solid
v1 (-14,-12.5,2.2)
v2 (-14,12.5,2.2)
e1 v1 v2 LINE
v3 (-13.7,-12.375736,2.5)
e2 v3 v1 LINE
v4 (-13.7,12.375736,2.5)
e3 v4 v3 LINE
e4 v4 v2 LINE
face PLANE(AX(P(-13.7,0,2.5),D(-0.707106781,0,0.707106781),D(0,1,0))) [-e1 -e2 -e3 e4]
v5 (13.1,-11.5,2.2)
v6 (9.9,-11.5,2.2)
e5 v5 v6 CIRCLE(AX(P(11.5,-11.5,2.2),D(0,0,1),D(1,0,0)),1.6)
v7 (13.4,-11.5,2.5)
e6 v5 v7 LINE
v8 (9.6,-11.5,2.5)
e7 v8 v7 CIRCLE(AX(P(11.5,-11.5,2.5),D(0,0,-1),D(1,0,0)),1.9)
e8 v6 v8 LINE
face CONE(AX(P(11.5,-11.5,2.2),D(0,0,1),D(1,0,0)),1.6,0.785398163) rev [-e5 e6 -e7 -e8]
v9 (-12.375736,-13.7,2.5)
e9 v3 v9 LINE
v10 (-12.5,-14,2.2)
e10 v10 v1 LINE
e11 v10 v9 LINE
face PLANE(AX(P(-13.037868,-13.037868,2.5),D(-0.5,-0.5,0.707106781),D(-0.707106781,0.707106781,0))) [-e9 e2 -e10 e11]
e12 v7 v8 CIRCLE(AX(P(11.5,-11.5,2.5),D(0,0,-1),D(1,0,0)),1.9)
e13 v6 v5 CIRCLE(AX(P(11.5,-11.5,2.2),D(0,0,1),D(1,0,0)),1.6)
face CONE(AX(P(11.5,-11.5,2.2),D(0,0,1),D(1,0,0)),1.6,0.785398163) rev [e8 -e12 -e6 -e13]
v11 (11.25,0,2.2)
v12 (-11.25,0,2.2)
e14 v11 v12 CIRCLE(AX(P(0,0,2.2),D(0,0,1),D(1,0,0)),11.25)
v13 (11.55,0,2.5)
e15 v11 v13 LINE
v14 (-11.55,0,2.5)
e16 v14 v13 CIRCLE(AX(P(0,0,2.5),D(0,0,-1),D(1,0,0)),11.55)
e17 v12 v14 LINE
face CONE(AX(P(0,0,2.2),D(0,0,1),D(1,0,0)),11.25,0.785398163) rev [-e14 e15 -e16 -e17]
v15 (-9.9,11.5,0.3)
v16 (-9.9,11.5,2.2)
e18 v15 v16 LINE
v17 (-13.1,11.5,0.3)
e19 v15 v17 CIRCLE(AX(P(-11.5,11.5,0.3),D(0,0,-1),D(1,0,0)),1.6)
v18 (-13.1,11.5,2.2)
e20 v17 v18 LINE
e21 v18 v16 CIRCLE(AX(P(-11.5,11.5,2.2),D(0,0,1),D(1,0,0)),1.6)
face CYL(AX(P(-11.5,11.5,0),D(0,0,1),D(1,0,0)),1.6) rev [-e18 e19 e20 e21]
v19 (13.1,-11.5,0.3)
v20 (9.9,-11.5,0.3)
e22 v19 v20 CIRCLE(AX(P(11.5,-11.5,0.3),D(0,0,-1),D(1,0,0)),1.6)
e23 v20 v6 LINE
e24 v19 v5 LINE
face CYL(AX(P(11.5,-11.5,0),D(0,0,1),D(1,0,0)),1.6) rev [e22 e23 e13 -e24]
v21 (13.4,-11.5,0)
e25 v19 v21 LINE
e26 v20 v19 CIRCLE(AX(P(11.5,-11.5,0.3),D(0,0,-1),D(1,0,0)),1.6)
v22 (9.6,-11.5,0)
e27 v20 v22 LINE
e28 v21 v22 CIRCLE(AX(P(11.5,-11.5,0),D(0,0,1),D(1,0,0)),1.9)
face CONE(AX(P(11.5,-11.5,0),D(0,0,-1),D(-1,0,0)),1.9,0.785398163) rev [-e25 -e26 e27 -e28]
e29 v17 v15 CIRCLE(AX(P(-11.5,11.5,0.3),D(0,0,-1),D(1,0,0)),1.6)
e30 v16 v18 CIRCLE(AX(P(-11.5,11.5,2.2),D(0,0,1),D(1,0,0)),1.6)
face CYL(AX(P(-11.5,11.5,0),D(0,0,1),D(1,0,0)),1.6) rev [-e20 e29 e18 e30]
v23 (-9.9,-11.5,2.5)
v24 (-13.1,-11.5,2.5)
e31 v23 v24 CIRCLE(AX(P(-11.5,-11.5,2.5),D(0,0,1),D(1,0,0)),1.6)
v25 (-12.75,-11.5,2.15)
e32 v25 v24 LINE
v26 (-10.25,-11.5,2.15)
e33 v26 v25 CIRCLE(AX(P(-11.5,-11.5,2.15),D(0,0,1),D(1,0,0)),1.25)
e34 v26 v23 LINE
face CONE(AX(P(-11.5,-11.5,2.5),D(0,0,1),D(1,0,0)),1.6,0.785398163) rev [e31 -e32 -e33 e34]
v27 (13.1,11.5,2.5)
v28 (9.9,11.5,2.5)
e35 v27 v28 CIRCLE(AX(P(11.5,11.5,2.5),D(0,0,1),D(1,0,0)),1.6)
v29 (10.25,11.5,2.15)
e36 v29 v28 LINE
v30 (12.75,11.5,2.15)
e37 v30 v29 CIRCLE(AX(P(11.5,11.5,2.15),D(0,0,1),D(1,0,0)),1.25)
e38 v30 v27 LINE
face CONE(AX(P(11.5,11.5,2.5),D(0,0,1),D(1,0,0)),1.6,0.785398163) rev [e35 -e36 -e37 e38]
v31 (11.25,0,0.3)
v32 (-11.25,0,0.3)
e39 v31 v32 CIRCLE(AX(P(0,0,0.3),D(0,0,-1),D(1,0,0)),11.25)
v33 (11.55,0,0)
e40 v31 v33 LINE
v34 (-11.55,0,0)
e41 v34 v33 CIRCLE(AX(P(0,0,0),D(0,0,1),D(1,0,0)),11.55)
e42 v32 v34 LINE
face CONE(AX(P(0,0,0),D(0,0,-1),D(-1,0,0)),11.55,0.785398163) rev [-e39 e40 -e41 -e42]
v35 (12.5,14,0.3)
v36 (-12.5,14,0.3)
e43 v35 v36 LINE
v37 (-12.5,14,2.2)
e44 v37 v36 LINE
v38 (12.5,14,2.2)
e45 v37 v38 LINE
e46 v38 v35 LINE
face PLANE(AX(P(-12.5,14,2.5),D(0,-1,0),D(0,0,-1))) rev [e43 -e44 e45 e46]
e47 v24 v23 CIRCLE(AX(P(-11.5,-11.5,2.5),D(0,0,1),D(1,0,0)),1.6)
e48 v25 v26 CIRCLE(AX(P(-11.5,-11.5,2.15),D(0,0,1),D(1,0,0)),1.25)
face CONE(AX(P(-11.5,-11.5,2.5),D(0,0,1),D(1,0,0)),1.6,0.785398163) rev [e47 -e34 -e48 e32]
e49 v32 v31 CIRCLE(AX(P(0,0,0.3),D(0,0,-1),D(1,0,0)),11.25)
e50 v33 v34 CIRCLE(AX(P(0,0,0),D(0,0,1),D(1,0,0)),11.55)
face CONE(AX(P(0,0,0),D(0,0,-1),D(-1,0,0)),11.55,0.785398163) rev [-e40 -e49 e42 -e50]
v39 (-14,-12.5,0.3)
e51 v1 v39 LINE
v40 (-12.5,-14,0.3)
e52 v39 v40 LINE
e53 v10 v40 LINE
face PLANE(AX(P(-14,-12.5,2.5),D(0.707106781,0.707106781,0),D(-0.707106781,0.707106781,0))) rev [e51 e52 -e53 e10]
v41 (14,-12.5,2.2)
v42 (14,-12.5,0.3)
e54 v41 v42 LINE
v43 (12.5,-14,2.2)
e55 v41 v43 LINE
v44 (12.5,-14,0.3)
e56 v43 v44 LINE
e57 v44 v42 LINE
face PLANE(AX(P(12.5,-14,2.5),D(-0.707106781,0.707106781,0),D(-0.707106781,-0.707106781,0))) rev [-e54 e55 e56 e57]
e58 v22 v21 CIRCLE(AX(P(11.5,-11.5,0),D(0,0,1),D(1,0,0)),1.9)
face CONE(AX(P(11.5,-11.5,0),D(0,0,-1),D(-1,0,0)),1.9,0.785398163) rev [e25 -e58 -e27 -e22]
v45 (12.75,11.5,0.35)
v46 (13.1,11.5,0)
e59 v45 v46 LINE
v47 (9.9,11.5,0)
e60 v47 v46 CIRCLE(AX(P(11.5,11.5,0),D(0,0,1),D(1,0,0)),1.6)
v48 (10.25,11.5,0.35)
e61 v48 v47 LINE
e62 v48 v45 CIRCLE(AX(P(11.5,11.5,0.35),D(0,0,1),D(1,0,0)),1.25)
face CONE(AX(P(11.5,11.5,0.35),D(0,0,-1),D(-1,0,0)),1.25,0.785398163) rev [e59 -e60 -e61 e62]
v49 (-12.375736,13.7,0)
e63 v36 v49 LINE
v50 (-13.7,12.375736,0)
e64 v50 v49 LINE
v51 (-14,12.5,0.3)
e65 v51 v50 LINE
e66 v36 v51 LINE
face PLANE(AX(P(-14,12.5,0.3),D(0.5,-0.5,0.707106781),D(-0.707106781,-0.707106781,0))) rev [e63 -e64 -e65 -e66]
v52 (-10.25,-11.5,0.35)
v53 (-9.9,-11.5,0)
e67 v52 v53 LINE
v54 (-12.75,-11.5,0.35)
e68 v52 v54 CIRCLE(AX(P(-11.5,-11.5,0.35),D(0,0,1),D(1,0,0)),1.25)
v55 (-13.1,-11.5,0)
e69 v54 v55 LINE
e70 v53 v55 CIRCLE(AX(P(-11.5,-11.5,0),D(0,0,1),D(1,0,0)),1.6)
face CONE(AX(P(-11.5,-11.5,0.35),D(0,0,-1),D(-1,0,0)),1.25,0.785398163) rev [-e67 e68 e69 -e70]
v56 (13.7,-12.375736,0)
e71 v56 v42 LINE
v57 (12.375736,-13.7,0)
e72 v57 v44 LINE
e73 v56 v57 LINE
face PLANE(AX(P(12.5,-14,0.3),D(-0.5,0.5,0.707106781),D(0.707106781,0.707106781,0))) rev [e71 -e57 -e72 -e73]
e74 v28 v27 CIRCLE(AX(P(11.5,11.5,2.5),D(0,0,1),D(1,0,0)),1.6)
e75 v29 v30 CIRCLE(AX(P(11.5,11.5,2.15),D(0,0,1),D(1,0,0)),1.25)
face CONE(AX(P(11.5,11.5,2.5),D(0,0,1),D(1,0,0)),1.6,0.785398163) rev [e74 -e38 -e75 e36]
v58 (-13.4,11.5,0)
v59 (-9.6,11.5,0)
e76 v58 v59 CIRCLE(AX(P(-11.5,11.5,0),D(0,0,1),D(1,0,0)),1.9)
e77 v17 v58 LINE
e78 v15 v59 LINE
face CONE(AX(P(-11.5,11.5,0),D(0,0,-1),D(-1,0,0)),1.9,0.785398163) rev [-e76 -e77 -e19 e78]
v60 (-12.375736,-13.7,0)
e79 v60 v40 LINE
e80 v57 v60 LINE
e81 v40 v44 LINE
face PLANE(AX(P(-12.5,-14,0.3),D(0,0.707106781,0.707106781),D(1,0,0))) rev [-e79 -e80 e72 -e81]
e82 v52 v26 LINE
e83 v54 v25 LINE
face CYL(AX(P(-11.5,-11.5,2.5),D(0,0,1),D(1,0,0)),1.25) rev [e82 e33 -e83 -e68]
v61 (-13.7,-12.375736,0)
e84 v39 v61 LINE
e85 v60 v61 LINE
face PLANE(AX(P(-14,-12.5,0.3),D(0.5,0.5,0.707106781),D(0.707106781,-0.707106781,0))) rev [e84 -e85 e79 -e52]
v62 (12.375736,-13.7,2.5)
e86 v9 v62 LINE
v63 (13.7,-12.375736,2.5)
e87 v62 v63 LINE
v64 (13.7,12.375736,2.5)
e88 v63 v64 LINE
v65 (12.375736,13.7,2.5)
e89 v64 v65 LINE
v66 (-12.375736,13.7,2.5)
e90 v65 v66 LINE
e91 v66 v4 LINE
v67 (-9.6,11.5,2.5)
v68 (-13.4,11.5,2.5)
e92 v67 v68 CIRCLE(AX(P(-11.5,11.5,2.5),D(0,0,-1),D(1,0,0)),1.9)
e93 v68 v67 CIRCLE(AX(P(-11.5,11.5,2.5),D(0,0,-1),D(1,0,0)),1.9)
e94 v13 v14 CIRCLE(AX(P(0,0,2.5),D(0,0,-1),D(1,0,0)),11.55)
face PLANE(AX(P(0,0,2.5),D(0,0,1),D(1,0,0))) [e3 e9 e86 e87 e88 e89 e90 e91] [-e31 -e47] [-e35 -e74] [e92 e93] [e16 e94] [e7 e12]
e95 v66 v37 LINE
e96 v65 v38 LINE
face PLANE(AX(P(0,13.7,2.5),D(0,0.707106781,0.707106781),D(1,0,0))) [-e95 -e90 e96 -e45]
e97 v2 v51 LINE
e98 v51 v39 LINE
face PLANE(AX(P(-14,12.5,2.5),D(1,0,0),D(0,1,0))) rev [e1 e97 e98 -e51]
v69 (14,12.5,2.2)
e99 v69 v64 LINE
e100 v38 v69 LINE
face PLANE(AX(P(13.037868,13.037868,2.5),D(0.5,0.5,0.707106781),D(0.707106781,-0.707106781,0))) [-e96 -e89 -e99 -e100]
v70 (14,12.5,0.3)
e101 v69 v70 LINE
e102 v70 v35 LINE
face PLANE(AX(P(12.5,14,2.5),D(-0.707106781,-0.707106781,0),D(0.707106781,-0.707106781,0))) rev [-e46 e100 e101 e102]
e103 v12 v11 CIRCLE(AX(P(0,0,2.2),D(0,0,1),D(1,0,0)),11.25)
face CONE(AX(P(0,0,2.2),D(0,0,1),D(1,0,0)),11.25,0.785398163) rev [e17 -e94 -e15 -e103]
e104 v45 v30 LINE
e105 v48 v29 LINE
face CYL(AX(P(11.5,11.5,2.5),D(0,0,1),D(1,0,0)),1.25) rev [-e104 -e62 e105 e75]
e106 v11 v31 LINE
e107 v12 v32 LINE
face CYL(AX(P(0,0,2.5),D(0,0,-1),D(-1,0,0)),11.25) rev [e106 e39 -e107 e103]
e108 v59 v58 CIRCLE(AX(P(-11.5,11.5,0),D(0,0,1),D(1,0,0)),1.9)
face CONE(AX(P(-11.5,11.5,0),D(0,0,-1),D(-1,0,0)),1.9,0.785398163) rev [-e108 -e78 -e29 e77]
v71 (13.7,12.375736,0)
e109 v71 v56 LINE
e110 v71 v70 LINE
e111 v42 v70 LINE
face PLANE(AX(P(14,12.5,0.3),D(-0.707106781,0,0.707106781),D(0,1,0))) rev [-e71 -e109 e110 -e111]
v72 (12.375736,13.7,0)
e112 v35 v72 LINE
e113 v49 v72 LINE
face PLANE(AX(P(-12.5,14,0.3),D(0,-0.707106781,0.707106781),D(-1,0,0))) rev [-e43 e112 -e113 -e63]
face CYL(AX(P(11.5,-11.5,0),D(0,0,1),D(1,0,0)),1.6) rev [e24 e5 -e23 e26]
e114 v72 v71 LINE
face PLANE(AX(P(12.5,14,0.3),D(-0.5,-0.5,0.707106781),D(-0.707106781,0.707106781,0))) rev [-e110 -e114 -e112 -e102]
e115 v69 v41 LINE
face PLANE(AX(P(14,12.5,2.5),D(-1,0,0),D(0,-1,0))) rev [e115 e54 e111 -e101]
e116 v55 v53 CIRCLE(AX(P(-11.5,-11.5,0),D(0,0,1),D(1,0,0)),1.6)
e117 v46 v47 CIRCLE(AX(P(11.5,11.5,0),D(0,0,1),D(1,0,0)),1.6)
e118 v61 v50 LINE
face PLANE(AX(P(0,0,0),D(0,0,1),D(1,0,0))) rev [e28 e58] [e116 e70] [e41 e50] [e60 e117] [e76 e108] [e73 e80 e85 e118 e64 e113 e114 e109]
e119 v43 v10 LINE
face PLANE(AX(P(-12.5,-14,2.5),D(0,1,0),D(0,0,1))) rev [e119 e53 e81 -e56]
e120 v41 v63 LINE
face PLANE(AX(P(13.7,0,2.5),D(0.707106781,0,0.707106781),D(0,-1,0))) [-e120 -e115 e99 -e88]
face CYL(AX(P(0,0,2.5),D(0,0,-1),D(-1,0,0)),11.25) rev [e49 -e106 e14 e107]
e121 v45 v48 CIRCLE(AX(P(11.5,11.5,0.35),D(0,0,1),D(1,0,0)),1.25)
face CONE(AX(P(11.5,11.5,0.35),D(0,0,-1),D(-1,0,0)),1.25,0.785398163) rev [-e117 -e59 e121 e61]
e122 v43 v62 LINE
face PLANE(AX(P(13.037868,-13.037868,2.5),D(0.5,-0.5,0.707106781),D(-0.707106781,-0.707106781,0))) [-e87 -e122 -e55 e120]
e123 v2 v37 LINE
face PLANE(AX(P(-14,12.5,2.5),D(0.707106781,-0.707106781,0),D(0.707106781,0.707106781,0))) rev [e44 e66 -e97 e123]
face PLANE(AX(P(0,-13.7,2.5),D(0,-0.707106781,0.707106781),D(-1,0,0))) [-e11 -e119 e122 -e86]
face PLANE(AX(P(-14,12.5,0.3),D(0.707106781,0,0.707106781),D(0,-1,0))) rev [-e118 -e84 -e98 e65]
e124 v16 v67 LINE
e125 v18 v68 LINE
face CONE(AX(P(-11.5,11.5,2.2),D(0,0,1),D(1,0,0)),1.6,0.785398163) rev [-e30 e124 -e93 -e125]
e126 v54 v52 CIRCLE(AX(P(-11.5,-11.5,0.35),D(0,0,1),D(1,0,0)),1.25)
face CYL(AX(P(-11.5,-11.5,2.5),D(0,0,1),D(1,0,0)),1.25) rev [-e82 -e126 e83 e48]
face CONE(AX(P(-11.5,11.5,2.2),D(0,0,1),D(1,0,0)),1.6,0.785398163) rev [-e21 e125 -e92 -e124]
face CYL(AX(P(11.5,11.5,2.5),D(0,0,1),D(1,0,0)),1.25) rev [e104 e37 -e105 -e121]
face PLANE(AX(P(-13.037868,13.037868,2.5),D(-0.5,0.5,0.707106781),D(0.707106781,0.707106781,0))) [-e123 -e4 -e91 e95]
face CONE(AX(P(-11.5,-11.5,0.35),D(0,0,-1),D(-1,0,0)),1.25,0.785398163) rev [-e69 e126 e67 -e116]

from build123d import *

# Parameters (mm, degrees)
SKETCH1_R                  = 11.25
BOSS_EXTRUDE1_DEPTH        = 2.5
SKETCH2_R                  = 1.6
CUT_EXTRUDE1_DEPTH         = 2.5
M3_TAPPED_HOLE1_AT_2_COUNT = 2
M3_TAPPED_HOLE1_AT_2_PITCH = 32.526911935
CHAMFER1_SIZE              = 0.3


with BuildPart() as part:
    # Sketch1 → Boss-Extrude1 (new body)
    with BuildSketch(Plane.XY):
        Polygon((-14, -12.5), (-12.5, -14), (12.5, -14), (14, -12.5), (14, 12.5), (12.5, 14), (-12.5, 14), (-14, 12.5), align=None)
        Circle(SKETCH1_R, mode=Mode.SUBTRACT)
    extrude(amount=BOSS_EXTRUDE1_DEPTH)

    # Sketch2 → Cut-Extrude1 (cut)
    with BuildSketch(Plane.XY.offset(2.5)):
        with Locations((-11.5, 11.5)):
            Circle(SKETCH2_R)
        with Locations((11.5, -11.5)):
            Circle(SKETCH2_R)
    extrude(amount=-CUT_EXTRUDE1_DEPTH, mode=Mode.SUBTRACT)

    # Sketch4 → M3 Tapped Hole1 (revolve, cut)
    with BuildSketch(Plane(origin=(-11.5, -11.5, 2.5), x_dir=(0, -1, 0), z_dir=(1, 0, 0))):
        Polygon((0, 0), (0, 2.5), (1.6, 2.5), (1.25, 2.15), (1.25, 0.35), (1.6, 0), align=None)
    m3_tapped_hole1 = revolve(axis=Axis((-11.5, -11.5, 8.85), (0, 0, -1)), mode=Mode.SUBTRACT)

    # M3 Tapped Hole1 at 2: M3 Tapped Hole1 ×2
    with Locations(*[Vector(0.7071067811865476, 0.7071067811865476, 0) * (i * M3_TAPPED_HOLE1_AT_2_PITCH) for i in range(1, M3_TAPPED_HOLE1_AT_2_COUNT)]):
        add(m3_tapped_hole1, mode=Mode.SUBTRACT)

    # Chamfer1
    chamfer1_edges = [part.edges().sort_by_distance(p)[0] for p in [
        (13.25, -13.25, 0),
        (0, -14, 0),
        (-13.25, -13.25, 0),
        (-14, 0, 0),
        (0, -14, 2.5),
        (13.25, -13.25, 2.5),
        (14, 0, 2.5),
        (-11.25, 0, 0),
        (-11.25, 0, 2.5),
        (13.25, 13.25, 2.5),
        (0, 14, 2.5),
        (-13.1, 11.5, 0),
        (-13.1, 11.5, 2.5),
        (-13.25, 13.25, 2.5),
        (9.9, -11.5, 0),
        (9.9, -11.5, 2.5),
        (-14, 0, 2.5),
        (-13.25, 13.25, 0),
        (-13.25, -13.25, 2.5),
        (0, 14, 0),
        (13.25, 13.25, 0),
        (14, 0, 0),
    ]]
    chamfer(chamfer1_edges, length=CHAMFER1_SIZE)


solid = part.part
